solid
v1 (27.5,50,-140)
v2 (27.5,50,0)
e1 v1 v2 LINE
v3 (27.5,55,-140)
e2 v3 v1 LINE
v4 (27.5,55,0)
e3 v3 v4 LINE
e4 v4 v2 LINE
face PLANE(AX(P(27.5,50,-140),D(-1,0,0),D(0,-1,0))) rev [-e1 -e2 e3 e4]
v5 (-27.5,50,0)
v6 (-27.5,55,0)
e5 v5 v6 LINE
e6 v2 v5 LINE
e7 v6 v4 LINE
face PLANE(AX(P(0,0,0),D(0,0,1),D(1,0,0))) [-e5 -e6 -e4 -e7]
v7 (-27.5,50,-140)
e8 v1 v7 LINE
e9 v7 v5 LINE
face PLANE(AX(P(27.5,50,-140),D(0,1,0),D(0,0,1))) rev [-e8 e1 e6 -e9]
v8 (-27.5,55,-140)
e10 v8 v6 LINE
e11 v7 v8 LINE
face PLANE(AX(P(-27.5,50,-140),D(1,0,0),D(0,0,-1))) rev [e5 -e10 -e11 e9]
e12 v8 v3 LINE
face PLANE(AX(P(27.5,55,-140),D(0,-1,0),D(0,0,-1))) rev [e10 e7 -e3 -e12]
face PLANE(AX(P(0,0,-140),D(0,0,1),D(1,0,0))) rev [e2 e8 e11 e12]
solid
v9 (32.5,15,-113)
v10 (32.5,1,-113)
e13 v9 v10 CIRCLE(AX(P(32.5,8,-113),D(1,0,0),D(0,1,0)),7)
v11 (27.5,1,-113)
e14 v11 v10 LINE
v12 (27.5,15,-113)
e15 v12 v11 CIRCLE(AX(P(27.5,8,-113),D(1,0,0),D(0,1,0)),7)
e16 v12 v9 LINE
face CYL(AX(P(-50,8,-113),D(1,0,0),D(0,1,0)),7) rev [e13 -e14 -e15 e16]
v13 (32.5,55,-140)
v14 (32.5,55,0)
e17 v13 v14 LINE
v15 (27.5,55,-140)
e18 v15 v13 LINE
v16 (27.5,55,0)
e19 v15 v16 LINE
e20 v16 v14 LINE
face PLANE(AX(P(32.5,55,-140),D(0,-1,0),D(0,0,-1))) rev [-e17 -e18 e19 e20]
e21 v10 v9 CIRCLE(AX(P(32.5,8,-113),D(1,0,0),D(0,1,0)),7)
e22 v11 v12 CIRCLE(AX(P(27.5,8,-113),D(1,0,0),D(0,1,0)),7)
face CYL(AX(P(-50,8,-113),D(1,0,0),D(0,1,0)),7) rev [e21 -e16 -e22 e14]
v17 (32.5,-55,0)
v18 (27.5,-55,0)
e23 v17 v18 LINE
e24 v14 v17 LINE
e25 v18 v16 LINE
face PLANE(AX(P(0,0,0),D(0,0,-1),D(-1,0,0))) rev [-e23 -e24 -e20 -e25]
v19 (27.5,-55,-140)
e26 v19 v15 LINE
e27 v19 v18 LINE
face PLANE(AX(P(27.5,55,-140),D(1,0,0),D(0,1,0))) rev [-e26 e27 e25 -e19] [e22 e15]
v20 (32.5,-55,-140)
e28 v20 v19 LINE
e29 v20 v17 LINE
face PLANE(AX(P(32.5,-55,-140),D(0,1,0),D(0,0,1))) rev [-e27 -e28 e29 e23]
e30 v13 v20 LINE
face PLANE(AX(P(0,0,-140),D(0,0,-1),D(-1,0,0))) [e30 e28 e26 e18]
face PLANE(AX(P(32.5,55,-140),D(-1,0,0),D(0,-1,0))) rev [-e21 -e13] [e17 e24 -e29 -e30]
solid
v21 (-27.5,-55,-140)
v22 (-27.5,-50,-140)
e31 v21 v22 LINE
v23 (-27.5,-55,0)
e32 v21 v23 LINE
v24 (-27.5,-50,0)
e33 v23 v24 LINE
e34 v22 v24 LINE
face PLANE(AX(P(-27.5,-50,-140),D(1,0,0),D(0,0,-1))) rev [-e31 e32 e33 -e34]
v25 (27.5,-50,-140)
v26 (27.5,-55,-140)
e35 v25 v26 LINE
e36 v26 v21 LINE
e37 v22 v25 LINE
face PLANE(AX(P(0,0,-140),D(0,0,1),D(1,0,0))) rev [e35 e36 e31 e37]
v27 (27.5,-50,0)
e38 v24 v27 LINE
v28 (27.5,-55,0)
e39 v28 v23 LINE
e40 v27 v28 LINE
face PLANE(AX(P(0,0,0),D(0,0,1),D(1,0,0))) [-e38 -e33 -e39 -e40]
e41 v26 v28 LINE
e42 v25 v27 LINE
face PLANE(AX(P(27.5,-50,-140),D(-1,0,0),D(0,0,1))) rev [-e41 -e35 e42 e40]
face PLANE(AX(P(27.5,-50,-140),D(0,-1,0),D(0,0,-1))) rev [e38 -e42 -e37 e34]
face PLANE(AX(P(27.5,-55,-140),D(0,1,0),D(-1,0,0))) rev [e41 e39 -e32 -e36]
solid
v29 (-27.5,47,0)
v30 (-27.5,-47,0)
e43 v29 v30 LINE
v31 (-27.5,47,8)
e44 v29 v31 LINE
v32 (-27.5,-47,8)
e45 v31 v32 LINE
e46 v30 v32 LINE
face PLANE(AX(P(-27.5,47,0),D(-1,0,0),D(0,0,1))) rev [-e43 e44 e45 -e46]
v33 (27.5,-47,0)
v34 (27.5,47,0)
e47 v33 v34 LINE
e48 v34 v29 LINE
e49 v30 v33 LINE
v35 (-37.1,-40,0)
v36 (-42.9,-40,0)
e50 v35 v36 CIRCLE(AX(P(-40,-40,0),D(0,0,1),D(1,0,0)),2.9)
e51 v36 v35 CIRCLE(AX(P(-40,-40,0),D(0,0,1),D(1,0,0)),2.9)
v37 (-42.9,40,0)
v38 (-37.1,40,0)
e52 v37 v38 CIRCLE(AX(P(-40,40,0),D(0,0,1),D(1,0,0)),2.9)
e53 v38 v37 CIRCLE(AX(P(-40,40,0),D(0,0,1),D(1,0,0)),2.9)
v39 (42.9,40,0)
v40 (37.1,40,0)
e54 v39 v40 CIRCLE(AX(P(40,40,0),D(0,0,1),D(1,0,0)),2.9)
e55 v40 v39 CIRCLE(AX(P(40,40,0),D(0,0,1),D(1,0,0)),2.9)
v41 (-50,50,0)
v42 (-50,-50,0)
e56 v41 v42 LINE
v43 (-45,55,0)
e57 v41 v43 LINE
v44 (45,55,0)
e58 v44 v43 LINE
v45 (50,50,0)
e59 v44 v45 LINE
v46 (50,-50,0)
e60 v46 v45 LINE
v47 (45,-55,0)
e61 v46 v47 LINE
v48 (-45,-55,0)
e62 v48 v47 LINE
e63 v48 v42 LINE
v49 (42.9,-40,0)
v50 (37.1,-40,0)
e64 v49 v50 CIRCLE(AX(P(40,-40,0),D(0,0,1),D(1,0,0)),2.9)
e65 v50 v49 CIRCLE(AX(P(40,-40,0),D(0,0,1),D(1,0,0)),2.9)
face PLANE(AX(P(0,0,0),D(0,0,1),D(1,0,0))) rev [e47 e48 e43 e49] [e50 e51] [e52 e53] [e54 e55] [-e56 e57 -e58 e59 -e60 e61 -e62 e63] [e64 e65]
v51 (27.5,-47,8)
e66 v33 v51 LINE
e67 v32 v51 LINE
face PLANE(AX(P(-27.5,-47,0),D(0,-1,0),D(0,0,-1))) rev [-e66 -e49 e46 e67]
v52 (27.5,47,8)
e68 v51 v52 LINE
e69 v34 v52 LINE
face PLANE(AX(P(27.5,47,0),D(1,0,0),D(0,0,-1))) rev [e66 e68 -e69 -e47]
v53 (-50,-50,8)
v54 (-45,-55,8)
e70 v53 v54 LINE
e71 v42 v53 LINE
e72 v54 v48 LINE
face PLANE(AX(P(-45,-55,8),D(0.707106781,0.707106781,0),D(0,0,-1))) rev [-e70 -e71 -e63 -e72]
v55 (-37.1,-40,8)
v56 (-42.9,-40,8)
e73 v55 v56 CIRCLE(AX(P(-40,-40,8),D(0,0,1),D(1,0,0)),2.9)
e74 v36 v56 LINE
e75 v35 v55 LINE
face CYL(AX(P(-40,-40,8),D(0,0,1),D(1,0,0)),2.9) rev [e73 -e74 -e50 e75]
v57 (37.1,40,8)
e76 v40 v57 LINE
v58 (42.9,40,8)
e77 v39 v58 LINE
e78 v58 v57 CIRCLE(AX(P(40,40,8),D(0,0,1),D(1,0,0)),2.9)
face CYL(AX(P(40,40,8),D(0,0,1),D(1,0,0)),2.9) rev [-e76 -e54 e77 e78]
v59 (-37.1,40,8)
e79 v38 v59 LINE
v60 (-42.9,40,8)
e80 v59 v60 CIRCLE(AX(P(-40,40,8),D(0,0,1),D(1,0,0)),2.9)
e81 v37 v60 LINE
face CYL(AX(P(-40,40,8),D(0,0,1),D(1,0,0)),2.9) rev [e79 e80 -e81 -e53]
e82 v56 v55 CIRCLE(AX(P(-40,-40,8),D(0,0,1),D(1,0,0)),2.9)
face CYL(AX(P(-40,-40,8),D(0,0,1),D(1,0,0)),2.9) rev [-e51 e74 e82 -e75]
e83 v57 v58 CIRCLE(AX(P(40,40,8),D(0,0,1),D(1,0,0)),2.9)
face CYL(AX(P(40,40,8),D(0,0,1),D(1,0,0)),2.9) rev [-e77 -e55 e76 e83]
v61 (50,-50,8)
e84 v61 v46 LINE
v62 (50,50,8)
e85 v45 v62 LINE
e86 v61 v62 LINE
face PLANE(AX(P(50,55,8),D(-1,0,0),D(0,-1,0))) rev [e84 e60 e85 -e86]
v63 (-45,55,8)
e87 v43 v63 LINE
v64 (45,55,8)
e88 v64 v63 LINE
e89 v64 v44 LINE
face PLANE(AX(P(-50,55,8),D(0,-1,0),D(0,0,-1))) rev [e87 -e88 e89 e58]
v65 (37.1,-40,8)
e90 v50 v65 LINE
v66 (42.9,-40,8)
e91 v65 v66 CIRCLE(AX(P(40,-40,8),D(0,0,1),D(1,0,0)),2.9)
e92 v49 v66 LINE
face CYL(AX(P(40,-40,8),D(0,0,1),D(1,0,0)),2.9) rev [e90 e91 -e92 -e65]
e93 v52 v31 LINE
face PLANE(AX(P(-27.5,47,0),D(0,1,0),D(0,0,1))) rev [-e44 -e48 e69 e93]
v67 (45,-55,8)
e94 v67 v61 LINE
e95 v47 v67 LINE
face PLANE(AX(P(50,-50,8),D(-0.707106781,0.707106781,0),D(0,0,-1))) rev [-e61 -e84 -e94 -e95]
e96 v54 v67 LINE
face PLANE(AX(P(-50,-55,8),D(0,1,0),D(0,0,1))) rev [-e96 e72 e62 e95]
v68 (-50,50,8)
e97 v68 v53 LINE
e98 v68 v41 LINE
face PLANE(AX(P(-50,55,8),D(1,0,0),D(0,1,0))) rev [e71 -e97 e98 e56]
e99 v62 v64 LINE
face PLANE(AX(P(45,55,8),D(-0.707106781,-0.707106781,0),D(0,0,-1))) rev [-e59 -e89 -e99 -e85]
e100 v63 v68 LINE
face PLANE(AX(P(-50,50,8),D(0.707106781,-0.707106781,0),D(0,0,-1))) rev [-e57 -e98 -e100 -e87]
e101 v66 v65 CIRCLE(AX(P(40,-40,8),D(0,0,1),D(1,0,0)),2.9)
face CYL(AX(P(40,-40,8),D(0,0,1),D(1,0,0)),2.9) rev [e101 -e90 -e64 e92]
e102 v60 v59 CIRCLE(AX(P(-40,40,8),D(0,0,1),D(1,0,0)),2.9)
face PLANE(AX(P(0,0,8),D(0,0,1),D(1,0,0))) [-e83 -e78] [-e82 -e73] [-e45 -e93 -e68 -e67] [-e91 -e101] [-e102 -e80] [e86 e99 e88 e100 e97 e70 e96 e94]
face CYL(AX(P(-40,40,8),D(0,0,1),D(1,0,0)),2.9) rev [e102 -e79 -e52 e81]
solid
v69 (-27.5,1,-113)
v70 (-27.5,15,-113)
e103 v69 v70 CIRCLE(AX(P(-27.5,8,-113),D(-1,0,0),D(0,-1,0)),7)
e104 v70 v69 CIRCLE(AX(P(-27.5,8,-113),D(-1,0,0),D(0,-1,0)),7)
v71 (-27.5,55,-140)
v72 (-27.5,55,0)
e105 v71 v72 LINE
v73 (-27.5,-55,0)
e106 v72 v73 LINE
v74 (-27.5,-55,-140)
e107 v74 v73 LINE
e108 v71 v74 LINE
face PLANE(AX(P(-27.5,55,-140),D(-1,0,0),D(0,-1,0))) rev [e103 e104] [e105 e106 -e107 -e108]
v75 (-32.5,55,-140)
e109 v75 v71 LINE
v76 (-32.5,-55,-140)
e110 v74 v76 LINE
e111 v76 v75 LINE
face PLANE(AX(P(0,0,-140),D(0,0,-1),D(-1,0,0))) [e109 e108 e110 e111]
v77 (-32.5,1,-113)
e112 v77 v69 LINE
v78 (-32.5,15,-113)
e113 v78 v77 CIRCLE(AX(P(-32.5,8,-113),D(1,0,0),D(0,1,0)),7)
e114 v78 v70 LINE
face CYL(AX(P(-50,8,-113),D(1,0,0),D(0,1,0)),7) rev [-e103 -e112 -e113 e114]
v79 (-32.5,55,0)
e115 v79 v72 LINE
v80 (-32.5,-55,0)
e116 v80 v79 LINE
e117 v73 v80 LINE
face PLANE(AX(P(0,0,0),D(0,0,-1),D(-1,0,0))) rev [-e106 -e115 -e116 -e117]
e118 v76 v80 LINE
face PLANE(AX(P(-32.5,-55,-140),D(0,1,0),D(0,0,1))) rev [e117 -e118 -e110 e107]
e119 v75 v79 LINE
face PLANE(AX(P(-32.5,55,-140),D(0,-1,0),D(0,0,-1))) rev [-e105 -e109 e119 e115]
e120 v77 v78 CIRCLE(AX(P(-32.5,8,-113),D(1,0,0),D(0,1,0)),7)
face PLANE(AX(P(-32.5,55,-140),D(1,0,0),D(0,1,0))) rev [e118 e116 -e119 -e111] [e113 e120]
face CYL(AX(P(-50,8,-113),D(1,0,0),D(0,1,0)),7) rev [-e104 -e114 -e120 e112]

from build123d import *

# Parameters (mm, degrees)
SKETCH1_W                     = 100
SKETCH1_H                     = 110
BOSS_EXTRUDE1_DEPTH           = 8
SKETCH2_W                     = 55
SKETCH2_H                     = 94
CUT_EXTRUDE1_DEPTH            = 8
SKETCH3_W                     = 5
SKETCH3_H                     = 110
BOSS_EXTRUDE2_DEPTH           = 140
BOSS_EXTRUDE2_2_DEPTH         = 140
SKETCH4_W                     = 55
SKETCH4_H                     = 5
BOSS_EXTRUDE3_DEPTH           = 140
BOSS_EXTRUDE3_2_DEPTH         = 140
CHAMFER1_SIZE                 = 5
SKETCH6_W                     = 2.9
SKETCH6_H                     = 148
M5_CLEARANCE_HOLE1_AT_2_COUNT = 2
M5_CLEARANCE_HOLE1_AT_2_PITCH = 80
M5_CLEARANCE_HOLE1_AT_3_COUNT = 2
M5_CLEARANCE_HOLE1_AT_3_PITCH = 113.13708499
M5_CLEARANCE_HOLE1_AT_4_COUNT = 2
M5_CLEARANCE_HOLE1_AT_4_PITCH = 80
SKETCH7_R                     = 7
CUT_EXTRUDE2_DEPTH            = 172.555384643


with BuildPart() as part:
    # Sketch1 → Boss-Extrude1 (new body)
    with BuildSketch(Plane.XY):
        Rectangle(SKETCH1_W, SKETCH1_H)
    extrude(amount=BOSS_EXTRUDE1_DEPTH)

    # Sketch2 → Cut-Extrude1 (cut)
    with BuildSketch(Plane.XY.offset(8)):
        Rectangle(SKETCH2_W, SKETCH2_H)
    extrude(amount=-CUT_EXTRUDE1_DEPTH, mode=Mode.SUBTRACT)

    # Chamfer1
    chamfer1_edges = [part.edges().sort_by_distance(p)[0] for p in [
        (50, -55, 4),
        (-50, -55, 4),
        (-50, 55, 4),
        (50, 55, 4),
    ]]
    chamfer(chamfer1_edges, length=CHAMFER1_SIZE)

    # Sketch6 → M5 Clearance Hole1 (revolve, cut)
    with BuildSketch(Plane(origin=(-40, 40, 8), x_dir=(0, -1, 0), z_dir=(1, 0, 0))):
        with Locations((1.45, 74)):
            Rectangle(SKETCH6_W, SKETCH6_H)
    m5_clearance_hole1 = revolve(axis=Axis((-40, 40, 14.35), (0, 0, -1)), mode=Mode.SUBTRACT)

    # M5 Clearance Hole1 at 2: M5 Clearance Hole1 ×2
    with Locations(*[(0, -i * M5_CLEARANCE_HOLE1_AT_2_PITCH, 0) for i in range(1, M5_CLEARANCE_HOLE1_AT_2_COUNT)]):
        add(m5_clearance_hole1, mode=Mode.SUBTRACT)

    # M5 Clearance Hole1 at 3: M5 Clearance Hole1 ×2
    with Locations(*[Vector(0.7071067811865476, -0.7071067811865476, 0) * (i * M5_CLEARANCE_HOLE1_AT_3_PITCH) for i in range(1, M5_CLEARANCE_HOLE1_AT_3_COUNT)]):
        add(m5_clearance_hole1, mode=Mode.SUBTRACT)

    # M5 Clearance Hole1 at 4: M5 Clearance Hole1 ×2
    with Locations(*[(i * M5_CLEARANCE_HOLE1_AT_4_PITCH, 0, 0) for i in range(1, M5_CLEARANCE_HOLE1_AT_4_COUNT)]):
        add(m5_clearance_hole1, mode=Mode.SUBTRACT)


with BuildPart() as body_2:
    # Sketch3 → Boss-Extrude2 (new body)
    with BuildSketch(Plane(origin=(0, 0, 0), x_dir=(-1, 0, 0), z_dir=(0, 0, -1))):
        with Locations((-30, 0)):
            Rectangle(SKETCH3_W, SKETCH3_H)
    extrude(amount=BOSS_EXTRUDE2_DEPTH)


with BuildPart() as body_3:
    # Sketch3 → Boss-Extrude2 2 (new body)
    with BuildSketch(Plane(origin=(0, 0, 0), x_dir=(-1, 0, 0), z_dir=(0, 0, -1))):
        with Locations((30, 0)):
            Rectangle(SKETCH3_W, SKETCH3_H)
    extrude(amount=BOSS_EXTRUDE2_2_DEPTH)


with BuildPart() as body_4:
    # Sketch4 → Boss-Extrude3 (new body)
    with BuildSketch(Plane(origin=(0, 0, 0), x_dir=(-1, 0, 0), z_dir=(0, 0, -1))):
        with Locations((0, 52.5)):
            Rectangle(SKETCH4_W, SKETCH4_H)
    extrude(amount=BOSS_EXTRUDE3_DEPTH)


with BuildPart() as body_5:
    # Sketch4 → Boss-Extrude3 2 (new body)
    with BuildSketch(Plane(origin=(0, 0, 0), x_dir=(-1, 0, 0), z_dir=(0, 0, -1))):
        with Locations((0, -52.5)):
            Rectangle(SKETCH4_W, SKETCH4_H)
    extrude(amount=BOSS_EXTRUDE3_2_DEPTH)


with BuildPart() as cut_extrude2_tool:
    # Sketch7 → Cut-Extrude2 (new, through all)
    with BuildSketch(Plane(origin=(32.5, 0, 0), x_dir=(0, 0, -1), z_dir=(1, 0, 0))):
        with Locations(Location((113, 8, 0), (0, 0, 90))):
            Circle(SKETCH7_R)
    extrude(amount=-CUT_EXTRUDE2_DEPTH)


with BuildPart() as body_2_1:
    add(body_2.part)

    # Cut-Extrude2: cut by cut_extrude2_tool
    add(cut_extrude2_tool.part, mode=Mode.SUBTRACT)


with BuildPart() as body_3_1:
    add(body_3.part)

    # Cut-Extrude2: cut by cut_extrude2_tool
    add(cut_extrude2_tool.part, mode=Mode.SUBTRACT)


solid = Compound([part.part, body_4.part, body_5.part, body_2_1.part, body_3_1.part])
